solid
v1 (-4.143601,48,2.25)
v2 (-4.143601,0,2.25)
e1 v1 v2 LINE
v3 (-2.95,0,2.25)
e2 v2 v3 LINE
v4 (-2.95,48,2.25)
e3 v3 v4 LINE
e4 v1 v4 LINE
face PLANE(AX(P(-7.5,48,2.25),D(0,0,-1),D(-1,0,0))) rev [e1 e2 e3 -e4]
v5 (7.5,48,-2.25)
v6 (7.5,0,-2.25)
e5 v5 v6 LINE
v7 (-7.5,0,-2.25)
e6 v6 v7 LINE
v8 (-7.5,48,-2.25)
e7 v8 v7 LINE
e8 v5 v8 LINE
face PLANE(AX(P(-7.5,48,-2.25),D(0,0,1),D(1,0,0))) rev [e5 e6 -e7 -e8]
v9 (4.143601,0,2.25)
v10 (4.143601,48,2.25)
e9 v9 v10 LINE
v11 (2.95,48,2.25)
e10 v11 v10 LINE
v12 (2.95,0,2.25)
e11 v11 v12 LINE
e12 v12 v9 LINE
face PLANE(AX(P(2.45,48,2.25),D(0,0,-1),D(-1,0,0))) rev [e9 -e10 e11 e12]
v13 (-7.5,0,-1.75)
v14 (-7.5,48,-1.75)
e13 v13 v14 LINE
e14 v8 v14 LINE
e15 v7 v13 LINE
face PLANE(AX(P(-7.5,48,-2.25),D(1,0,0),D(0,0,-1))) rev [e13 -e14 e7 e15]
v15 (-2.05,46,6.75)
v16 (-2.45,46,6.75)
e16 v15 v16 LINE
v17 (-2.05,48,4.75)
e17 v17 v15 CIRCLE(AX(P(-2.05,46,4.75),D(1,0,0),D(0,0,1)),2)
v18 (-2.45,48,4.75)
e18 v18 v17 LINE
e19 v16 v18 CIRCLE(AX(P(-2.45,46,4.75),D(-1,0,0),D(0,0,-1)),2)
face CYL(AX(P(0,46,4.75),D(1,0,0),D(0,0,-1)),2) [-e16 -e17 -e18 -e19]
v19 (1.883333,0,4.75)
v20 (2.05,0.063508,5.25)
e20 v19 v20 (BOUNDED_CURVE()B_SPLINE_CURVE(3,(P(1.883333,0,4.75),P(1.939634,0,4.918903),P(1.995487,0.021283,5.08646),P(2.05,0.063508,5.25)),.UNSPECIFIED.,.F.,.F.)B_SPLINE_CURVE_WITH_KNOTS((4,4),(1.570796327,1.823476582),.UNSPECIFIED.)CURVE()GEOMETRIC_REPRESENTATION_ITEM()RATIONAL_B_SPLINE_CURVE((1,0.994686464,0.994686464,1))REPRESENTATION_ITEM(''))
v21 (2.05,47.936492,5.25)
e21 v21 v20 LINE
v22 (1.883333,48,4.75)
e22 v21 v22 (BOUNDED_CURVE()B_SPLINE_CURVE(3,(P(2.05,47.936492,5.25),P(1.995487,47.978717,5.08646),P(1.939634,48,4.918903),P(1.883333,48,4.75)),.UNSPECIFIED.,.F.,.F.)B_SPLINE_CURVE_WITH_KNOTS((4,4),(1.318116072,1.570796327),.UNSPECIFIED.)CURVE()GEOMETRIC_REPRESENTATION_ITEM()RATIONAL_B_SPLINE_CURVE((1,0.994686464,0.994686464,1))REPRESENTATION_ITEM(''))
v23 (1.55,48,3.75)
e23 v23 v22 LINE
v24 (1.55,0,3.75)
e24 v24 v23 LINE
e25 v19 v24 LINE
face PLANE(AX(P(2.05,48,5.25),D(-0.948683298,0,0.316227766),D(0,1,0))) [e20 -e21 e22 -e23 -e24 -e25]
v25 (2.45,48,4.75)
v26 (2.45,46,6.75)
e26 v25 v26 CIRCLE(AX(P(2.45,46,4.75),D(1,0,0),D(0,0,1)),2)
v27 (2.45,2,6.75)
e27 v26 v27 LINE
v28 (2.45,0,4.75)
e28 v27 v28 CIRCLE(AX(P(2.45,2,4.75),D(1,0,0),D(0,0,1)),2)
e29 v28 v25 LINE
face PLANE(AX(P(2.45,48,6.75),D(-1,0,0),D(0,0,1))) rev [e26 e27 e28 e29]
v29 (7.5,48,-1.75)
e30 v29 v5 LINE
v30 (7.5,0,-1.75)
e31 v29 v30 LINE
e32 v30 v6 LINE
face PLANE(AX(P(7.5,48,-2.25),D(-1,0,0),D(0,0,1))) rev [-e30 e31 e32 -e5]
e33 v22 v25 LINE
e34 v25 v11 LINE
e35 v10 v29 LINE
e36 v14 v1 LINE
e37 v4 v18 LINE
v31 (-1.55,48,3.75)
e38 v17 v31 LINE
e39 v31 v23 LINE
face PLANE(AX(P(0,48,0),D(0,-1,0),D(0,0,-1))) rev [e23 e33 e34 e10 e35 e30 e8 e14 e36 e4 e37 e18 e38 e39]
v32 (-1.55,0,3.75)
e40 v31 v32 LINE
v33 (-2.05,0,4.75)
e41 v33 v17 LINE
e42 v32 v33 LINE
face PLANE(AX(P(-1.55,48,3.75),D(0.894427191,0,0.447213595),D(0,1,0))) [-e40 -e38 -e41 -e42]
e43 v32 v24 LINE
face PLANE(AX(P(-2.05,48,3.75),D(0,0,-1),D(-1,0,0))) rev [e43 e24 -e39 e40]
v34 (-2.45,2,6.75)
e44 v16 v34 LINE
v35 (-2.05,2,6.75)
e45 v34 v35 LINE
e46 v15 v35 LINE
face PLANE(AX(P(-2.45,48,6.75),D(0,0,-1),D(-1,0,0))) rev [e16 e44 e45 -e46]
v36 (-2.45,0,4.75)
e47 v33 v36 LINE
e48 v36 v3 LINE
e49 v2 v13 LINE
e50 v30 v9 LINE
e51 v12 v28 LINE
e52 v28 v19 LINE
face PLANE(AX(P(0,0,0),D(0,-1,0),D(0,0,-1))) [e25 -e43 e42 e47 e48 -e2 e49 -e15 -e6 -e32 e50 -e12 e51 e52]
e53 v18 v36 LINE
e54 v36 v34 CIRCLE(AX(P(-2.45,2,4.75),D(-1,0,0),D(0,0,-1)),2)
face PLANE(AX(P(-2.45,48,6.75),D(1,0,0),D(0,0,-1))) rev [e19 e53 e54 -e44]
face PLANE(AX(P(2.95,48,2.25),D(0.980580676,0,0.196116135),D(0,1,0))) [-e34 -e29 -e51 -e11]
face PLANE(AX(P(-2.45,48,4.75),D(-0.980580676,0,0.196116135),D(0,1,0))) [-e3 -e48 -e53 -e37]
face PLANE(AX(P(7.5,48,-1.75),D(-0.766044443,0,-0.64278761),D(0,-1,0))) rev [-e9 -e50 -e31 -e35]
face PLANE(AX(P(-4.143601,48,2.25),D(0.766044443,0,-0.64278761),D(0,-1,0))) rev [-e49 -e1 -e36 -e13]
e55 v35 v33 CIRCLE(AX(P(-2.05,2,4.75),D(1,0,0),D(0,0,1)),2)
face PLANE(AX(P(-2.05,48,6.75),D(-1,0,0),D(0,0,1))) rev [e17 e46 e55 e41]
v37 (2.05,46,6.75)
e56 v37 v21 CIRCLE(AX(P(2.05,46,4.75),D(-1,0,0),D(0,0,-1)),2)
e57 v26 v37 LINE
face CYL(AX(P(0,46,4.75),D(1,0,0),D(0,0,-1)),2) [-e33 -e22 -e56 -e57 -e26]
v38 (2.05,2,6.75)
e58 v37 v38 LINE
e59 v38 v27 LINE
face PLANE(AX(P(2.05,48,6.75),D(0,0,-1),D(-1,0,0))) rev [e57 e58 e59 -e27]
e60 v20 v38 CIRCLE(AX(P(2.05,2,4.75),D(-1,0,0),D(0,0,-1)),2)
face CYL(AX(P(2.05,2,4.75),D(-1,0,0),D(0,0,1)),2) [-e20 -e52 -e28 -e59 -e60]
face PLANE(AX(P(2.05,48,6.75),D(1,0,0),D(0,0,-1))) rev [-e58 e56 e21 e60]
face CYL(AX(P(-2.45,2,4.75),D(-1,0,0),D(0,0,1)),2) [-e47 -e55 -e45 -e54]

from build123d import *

# Parameters (mm, degrees)
BOSS_EXTRUDE1_DEPTH = 48
CHAMFER1_SIZE       = 1
CHAMFER1_SIZE2      = 0.5
CHAMFER2_SIZE       = 0.5
CHAMFER2_SIZE2      = 1.5
CHAMFER3_SIZE       = 0.5
CHAMFER3_SIZE2      = 2.5
CHAMFER4_SIZE       = 2.5
CHAMFER4_SIZE2      = 0.5
CHAMFER5_SIZE       = 4
CHAMFER5_SIZE2      = 3.356398525
CHAMFER6_SIZE       = 4
CHAMFER6_SIZE2      = 3.356398525
FILLET1_R           = 2


with BuildPart() as part:
    # Sketch1 → Boss-Extrude1 (new body)
    with BuildSketch(Plane(origin=(0, 0, 0), x_dir=(1, 0, 0), z_dir=(0, 1, 0))):
        Polygon((-7.5, 2.25), (7.5, 2.25), (7.5, -2.25), (2.45, -2.25), (2.45, -6.75), (2.05, -6.75), (2.05, -3.75), (-2.05, -3.75), (-2.05, -6.75), (-2.45, -6.75), (-2.45, -2.25), (-7.5, -2.25), align=None)
    extrude(amount=BOSS_EXTRUDE1_DEPTH)

    # Chamfer1
    chamfer1_edges = [part.edges().sort_by_distance(p)[0] for p in [
        (-2.05, 24, 3.75),
    ]]
    chamfer1_side = [part.faces().sort_by_distance(p)[0] for p in [
        (-2.05, 24, 5.25),
    ]]
    chamfer(chamfer1_edges, length=CHAMFER1_SIZE, length2=CHAMFER1_SIZE2, reference=chamfer1_side[0])

    # Chamfer2
    chamfer2_edges = [part.edges().sort_by_distance(p)[0] for p in [
        (2.05, 24, 3.75),
    ]]
    chamfer2_side = [part.faces().sort_by_distance(p)[0] for p in [
        (0.25, 24, 3.75),
    ]]
    chamfer(chamfer2_edges, length=CHAMFER2_SIZE, length2=CHAMFER2_SIZE2, reference=chamfer2_side[0])

    # Chamfer3
    chamfer3_edges = [part.edges().sort_by_distance(p)[0] for p in [
        (-2.45, 24, 2.25),
    ]]
    chamfer3_side = [part.faces().sort_by_distance(p)[0] for p in [
        (-4.975, 24, 2.25),
    ]]
    chamfer(chamfer3_edges, length=CHAMFER3_SIZE, length2=CHAMFER3_SIZE2, reference=chamfer3_side[0])

    # Chamfer4
    chamfer4_edges = [part.edges().sort_by_distance(p)[0] for p in [
        (2.45, 24, 2.25),
    ]]
    chamfer4_side = [part.faces().sort_by_distance(p)[0] for p in [
        (2.45, 24, 4.5),
    ]]
    chamfer(chamfer4_edges, length=CHAMFER4_SIZE, length2=CHAMFER4_SIZE2, reference=chamfer4_side[0])

    # Chamfer5
    chamfer5_edges = [part.edges().sort_by_distance(p)[0] for p in [
        (-7.5, 24, 2.25),
    ]]
    chamfer5_side = [part.faces().sort_by_distance(p)[0] for p in [
        (-7.5, 24, 0),
    ]]
    chamfer(chamfer5_edges, length=CHAMFER5_SIZE, length2=CHAMFER5_SIZE2, reference=chamfer5_side[0])

    # Chamfer6
    chamfer6_edges = [part.edges().sort_by_distance(p)[0] for p in [
        (7.5, 24, 2.25),
    ]]
    chamfer6_side = [part.faces().sort_by_distance(p)[0] for p in [
        (7.5, 24, 0),
    ]]
    chamfer(chamfer6_edges, length=CHAMFER6_SIZE, length2=CHAMFER6_SIZE2, reference=chamfer6_side[0])

    # Fillet1
    fillet1_edges = [part.edges().sort_by_distance(p)[0] for p in [
        (-2.25, 0, 6.75),
        (2.25, 0, 6.75),
        (-2.25, 48, 6.75),
        (2.25, 48, 6.75),
    ]]
    fillet(fillet1_edges, radius=FILLET1_R)


solid = part.part
